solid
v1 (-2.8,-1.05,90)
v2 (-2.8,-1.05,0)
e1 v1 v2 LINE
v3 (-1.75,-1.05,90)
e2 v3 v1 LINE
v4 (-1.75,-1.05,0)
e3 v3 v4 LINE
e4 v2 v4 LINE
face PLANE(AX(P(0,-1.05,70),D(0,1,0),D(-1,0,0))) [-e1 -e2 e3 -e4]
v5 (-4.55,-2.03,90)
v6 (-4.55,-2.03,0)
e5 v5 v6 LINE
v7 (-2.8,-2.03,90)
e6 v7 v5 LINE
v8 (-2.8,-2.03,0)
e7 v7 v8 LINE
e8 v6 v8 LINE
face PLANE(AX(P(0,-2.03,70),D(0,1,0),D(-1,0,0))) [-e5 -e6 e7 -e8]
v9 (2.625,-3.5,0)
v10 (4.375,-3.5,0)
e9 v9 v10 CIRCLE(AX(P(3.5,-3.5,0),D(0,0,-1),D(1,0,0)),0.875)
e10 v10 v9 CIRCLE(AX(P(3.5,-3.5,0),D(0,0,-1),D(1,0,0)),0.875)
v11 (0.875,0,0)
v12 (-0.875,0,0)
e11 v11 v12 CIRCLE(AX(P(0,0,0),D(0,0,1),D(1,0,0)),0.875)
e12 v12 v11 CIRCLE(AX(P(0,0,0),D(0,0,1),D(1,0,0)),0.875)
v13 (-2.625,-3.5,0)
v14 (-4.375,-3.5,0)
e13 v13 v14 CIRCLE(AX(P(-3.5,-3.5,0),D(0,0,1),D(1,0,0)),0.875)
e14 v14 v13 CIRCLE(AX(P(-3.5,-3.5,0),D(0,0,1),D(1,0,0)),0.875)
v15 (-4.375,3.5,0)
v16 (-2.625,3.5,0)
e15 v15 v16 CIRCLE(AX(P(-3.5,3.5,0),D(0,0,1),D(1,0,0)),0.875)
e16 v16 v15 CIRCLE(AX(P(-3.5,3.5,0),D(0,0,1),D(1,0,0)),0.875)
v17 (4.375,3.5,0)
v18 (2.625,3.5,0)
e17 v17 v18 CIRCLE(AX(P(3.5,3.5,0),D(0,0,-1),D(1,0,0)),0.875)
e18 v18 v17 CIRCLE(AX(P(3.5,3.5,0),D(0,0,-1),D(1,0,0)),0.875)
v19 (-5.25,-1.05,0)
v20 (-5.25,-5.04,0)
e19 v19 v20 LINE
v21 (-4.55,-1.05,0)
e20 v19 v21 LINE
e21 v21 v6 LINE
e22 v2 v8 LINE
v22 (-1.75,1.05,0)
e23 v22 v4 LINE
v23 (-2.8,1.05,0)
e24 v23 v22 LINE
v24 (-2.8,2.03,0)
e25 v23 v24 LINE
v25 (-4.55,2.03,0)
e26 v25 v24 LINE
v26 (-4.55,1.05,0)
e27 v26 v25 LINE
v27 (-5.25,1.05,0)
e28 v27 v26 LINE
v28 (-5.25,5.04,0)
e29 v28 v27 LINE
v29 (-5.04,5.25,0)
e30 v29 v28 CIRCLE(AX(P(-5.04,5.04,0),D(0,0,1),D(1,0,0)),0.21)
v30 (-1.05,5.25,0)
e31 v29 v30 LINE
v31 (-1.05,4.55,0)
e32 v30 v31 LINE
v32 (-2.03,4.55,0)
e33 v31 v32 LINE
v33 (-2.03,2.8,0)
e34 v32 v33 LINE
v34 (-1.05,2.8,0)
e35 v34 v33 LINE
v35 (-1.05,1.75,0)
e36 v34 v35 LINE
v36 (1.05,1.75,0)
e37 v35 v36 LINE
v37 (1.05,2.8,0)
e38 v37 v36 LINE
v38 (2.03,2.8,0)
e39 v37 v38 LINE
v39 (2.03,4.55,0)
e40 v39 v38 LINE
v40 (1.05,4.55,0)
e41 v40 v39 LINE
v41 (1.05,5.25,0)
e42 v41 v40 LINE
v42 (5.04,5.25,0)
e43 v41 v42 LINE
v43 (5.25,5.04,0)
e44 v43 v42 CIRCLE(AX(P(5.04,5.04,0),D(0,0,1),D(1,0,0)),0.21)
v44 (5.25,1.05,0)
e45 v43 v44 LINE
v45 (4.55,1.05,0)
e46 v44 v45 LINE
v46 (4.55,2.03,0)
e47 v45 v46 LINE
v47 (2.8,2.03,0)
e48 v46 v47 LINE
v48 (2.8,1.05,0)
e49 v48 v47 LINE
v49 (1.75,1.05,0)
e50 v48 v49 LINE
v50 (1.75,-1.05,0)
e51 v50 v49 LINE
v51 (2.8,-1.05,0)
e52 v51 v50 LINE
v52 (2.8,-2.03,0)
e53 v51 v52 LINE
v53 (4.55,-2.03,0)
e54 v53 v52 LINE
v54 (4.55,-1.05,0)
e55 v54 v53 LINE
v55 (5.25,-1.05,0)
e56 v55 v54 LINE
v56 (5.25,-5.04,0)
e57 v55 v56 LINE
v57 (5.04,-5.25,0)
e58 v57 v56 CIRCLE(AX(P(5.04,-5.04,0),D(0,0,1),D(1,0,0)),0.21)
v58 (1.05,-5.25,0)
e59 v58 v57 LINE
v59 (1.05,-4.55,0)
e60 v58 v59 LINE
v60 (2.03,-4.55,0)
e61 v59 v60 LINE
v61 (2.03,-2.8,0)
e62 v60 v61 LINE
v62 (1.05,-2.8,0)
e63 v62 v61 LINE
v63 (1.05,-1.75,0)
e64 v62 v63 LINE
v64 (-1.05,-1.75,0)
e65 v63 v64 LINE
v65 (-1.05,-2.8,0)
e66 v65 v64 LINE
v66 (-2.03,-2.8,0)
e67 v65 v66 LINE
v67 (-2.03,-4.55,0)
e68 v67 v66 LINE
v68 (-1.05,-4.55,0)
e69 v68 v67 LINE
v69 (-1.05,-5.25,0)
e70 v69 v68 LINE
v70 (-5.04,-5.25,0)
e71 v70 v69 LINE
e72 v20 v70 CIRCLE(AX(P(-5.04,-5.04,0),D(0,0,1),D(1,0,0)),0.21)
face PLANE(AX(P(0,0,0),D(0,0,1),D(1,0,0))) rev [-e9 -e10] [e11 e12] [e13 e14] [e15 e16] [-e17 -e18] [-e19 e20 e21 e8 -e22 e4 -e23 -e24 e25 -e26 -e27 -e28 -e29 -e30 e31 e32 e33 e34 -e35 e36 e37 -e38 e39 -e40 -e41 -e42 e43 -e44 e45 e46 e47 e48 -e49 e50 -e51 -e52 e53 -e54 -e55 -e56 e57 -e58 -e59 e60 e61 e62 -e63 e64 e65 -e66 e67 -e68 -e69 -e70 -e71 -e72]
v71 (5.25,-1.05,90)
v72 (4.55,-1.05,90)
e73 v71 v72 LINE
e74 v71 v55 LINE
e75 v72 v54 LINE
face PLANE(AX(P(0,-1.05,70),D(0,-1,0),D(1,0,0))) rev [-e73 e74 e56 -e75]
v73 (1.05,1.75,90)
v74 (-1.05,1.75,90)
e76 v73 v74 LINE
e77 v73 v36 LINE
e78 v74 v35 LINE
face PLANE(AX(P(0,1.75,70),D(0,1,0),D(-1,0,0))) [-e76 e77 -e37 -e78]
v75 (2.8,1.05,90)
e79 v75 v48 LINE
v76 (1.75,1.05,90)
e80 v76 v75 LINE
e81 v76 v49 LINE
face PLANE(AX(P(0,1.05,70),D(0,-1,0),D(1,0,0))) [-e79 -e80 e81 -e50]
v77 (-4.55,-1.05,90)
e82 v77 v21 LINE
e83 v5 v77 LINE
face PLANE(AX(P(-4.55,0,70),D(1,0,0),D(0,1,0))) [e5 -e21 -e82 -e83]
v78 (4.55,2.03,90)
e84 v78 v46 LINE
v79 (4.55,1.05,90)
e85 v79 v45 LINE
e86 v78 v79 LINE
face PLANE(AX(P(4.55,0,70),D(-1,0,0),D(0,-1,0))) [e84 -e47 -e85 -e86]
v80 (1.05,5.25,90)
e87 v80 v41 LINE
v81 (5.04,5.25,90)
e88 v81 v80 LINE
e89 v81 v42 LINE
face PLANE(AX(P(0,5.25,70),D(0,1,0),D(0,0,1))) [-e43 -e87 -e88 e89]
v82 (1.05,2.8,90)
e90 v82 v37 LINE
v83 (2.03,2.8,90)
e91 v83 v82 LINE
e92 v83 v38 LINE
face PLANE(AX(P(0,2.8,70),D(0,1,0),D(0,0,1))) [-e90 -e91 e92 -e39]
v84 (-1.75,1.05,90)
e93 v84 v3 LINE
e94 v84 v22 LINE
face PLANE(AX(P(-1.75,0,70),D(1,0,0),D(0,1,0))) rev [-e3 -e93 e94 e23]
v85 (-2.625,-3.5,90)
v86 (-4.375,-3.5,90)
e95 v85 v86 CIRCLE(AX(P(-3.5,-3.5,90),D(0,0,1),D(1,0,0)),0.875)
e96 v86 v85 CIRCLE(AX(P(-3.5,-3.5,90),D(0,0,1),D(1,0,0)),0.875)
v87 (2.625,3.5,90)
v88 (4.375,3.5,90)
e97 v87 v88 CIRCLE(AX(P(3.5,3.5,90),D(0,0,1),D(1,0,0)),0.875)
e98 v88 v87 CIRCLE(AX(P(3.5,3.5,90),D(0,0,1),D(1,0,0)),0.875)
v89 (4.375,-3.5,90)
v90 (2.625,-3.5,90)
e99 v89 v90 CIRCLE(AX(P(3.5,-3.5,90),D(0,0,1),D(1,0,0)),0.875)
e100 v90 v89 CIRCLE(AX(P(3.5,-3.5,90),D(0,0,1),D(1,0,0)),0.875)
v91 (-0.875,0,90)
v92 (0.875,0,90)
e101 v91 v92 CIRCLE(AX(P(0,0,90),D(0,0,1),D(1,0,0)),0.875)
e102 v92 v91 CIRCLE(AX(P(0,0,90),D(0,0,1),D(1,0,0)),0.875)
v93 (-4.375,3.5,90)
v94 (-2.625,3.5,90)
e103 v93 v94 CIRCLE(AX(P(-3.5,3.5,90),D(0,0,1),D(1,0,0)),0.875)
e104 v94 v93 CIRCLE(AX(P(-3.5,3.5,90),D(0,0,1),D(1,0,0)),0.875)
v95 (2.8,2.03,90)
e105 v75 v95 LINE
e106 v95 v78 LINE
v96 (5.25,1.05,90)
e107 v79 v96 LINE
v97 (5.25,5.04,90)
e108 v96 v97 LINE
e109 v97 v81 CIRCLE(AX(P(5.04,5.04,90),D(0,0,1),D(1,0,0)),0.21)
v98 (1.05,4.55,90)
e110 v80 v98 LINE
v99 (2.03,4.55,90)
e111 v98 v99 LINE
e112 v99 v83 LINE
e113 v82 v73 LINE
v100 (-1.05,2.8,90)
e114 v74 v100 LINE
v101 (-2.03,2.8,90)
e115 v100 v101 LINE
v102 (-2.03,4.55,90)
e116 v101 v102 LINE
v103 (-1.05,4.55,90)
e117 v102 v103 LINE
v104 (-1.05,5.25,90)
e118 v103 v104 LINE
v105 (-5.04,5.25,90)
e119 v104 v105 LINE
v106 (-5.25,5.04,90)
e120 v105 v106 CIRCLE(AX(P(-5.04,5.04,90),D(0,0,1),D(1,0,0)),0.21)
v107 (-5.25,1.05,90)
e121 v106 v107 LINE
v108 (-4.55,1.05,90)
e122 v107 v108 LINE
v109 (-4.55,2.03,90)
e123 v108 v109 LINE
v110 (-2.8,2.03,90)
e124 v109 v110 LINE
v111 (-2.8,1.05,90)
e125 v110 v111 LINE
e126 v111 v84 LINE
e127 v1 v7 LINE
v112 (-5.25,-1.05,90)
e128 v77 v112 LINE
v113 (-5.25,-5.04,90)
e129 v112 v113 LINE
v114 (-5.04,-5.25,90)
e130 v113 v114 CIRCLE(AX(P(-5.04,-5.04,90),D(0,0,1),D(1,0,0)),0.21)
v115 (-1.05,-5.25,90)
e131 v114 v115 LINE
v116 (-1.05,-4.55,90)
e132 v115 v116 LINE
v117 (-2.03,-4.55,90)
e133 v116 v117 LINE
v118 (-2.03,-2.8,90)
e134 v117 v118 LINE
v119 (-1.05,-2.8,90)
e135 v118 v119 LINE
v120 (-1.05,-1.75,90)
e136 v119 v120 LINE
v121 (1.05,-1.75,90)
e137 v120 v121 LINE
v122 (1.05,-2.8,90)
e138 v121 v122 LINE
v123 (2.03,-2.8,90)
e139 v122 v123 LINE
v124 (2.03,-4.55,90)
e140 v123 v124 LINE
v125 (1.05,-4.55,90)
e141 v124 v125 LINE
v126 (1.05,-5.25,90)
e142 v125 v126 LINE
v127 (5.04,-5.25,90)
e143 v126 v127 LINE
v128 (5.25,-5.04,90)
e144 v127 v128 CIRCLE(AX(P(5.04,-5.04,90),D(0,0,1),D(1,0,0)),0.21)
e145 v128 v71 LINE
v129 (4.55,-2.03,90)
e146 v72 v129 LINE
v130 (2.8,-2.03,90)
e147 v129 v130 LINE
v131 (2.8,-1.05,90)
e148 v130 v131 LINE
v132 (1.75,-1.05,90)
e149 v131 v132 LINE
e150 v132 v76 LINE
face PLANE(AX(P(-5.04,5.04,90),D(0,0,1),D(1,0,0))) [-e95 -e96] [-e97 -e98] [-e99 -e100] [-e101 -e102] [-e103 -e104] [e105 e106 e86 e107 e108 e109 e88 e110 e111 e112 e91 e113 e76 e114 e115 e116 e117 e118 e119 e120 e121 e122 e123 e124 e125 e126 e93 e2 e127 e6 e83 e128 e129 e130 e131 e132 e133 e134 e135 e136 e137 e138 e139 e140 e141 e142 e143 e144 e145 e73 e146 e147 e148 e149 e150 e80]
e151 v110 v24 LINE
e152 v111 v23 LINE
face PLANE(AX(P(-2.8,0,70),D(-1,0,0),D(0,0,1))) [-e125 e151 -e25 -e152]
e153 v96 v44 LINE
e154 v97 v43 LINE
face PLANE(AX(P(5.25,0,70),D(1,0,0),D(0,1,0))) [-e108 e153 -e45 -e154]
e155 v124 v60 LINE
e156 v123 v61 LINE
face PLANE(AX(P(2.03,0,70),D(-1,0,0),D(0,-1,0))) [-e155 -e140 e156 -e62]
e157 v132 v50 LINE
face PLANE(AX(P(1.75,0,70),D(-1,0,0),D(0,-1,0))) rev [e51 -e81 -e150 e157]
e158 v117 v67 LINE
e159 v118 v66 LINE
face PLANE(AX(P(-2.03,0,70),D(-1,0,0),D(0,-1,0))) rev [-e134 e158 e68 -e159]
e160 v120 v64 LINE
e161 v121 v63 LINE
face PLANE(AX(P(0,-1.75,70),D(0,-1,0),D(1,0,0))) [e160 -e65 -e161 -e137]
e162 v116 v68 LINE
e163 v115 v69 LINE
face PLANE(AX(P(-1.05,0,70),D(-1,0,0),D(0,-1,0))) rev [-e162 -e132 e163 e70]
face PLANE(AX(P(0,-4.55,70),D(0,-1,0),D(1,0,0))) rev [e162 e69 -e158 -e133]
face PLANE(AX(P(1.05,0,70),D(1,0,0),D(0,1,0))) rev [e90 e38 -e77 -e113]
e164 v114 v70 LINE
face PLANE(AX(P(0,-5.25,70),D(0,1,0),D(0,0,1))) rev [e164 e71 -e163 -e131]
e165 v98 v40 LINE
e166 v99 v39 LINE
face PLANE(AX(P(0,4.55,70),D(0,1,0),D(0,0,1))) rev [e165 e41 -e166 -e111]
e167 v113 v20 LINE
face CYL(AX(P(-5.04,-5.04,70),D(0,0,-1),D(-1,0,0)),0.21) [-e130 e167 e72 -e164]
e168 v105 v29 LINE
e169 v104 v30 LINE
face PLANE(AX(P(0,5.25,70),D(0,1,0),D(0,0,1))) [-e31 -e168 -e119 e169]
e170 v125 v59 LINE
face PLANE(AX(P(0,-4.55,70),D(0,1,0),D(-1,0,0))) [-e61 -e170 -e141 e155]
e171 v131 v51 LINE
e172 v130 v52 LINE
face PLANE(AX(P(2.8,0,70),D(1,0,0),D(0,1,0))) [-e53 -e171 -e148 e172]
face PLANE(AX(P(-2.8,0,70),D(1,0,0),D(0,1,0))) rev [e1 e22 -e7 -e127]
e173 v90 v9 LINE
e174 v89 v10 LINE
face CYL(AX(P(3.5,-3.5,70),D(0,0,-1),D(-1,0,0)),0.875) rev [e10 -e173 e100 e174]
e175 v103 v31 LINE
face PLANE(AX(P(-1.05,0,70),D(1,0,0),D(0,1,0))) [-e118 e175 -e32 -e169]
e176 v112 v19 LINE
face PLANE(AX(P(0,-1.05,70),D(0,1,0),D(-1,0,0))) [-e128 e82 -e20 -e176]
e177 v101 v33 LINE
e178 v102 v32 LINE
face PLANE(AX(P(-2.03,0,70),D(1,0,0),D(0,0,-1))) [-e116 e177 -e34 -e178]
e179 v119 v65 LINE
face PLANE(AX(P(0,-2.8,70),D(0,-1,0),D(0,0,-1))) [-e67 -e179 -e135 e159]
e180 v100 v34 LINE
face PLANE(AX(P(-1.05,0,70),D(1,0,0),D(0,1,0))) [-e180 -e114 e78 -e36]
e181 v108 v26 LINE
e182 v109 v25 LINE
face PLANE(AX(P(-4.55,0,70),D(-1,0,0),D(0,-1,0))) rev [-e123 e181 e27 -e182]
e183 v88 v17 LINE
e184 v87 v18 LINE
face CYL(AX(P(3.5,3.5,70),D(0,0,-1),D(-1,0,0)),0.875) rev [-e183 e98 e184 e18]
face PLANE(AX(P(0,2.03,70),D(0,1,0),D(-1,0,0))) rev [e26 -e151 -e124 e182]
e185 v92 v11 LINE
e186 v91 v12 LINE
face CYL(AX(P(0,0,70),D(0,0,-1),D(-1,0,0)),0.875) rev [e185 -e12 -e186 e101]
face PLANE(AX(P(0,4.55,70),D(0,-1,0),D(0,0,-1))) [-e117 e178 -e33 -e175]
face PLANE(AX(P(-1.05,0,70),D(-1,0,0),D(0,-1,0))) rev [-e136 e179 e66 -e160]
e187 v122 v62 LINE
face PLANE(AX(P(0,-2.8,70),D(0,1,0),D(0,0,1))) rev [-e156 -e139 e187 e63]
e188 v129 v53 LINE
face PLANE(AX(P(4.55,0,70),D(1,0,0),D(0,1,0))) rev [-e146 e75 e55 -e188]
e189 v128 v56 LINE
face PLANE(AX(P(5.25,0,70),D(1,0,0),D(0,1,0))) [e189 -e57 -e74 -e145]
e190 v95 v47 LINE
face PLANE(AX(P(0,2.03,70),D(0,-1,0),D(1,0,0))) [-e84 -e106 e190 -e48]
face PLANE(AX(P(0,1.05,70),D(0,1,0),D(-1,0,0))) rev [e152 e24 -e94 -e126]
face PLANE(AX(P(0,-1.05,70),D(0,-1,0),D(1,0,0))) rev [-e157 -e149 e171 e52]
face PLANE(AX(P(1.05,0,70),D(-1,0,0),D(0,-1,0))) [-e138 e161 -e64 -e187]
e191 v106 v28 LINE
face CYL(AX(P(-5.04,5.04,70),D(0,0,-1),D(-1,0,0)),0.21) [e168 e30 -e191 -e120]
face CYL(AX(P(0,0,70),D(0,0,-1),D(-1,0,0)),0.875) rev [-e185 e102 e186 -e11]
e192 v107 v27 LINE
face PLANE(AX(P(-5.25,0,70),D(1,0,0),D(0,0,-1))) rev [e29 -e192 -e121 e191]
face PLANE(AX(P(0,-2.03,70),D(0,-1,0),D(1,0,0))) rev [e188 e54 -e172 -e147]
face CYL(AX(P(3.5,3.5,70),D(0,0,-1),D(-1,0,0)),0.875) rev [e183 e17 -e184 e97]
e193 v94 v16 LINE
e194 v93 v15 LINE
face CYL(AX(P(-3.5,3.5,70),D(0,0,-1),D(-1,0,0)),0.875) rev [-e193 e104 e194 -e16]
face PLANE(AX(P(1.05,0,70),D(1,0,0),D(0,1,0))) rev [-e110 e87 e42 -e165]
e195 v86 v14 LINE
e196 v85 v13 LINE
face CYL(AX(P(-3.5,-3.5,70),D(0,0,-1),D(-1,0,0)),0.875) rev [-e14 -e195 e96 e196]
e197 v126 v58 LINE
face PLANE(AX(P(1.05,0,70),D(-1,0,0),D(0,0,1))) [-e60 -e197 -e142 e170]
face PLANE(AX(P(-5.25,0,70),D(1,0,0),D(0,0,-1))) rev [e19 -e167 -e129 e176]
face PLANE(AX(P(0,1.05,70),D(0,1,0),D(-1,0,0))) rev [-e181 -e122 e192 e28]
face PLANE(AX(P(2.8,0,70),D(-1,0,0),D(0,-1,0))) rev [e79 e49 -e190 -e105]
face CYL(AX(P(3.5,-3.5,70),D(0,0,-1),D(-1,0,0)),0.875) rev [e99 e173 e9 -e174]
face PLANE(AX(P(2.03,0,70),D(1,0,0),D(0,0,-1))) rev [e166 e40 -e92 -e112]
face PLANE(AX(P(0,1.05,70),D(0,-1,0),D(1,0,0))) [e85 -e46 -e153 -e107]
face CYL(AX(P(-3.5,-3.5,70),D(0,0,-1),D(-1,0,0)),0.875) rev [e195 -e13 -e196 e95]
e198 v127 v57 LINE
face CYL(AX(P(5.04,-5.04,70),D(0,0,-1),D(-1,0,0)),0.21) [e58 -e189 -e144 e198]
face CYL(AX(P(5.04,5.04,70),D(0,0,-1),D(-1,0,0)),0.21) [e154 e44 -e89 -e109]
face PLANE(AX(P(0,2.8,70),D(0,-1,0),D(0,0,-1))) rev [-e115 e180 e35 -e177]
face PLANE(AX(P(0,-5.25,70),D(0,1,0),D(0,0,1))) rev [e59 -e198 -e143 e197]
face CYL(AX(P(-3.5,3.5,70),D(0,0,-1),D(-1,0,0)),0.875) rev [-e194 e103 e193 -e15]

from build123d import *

# Parameters (mm, degrees)
SKETCH4_R           = 1.25
BOSS_EXTRUDE3_DEPTH = 100
SCALE_1_SCALE       = 0.7
SKETCH5_R           = 0.875
BOSS_EXTRUDE4_DEPTH = 20


with BuildPart() as part:
    # Sketch4 → Boss-Extrude3 (new body)
    with BuildSketch(Plane.XY):
        with BuildLine():
            Line((-1.5, 7.5), (-7.2, 7.5))
            ThreePointArc((-7.2, 7.5), (-7.412132034, 7.412132034), (-7.5, 7.2))
            Line((-7.5, 7.2), (-7.5, 1.5))
            Line((-7.5, 1.5), (-6.5, 1.5))
            Line((-6.5, 1.5), (-6.5, 2.9))
            Line((-6.5, 2.9), (-4, 2.9))
            Line((-4, 2.9), (-4, 1.5))
            Line((-4, 1.5), (-2.5, 1.5))
            Line((-2.5, 1.5), (-2.5, -1.5))
            Line((-2.5, -1.5), (-4, -1.5))
            Line((-4, -1.5), (-4, -2.9))
            Line((-4, -2.9), (-6.5, -2.9))
            Line((-6.5, -2.9), (-6.5, -1.5))
            Line((-6.5, -1.5), (-7.5, -1.5))
            Line((-7.5, -1.5), (-7.5, -7.2))
            ThreePointArc((-7.5, -7.2), (-7.412132034, -7.412132034), (-7.2, -7.5))
            Line((-7.2, -7.5), (-1.5, -7.5))
            Line((-1.5, -7.5), (-1.5, -6.5))
            Line((-1.5, -6.5), (-2.9, -6.5))
            Line((-2.9, -6.5), (-2.9, -4))
            Line((-2.9, -4), (-1.5, -4))
            Line((-1.5, -4), (-1.5, -2.5))
            Line((-1.5, -2.5), (1.5, -2.5))
            Line((1.5, -2.5), (1.5, -4))
            Line((1.5, -4), (2.9, -4))
            Line((2.9, -4), (2.9, -6.5))
            Line((2.9, -6.5), (1.5, -6.5))
            Line((1.5, -6.5), (1.5, -7.5))
            Line((1.5, -7.5), (7.2, -7.5))
            ThreePointArc((7.2, -7.5), (7.412132034, -7.412132034), (7.5, -7.2))
            Line((7.5, -7.2), (7.5, -1.5))
            Line((7.5, -1.5), (6.5, -1.5))
            Line((6.5, -1.5), (6.5, -2.9))
            Line((6.5, -2.9), (4, -2.9))
            Line((4, -2.9), (4, -1.5))
            Line((4, -1.5), (2.5, -1.5))
            Line((2.5, -1.5), (2.5, 1.5))
            Line((2.5, 1.5), (4, 1.5))
            Line((4, 1.5), (4, 2.9))
            Line((4, 2.9), (6.5, 2.9))
            Line((6.5, 2.9), (6.5, 1.5))
            Line((6.5, 1.5), (7.5, 1.5))
            Line((7.5, 1.5), (7.5, 7.2))
            ThreePointArc((7.5, 7.2), (7.412132034, 7.412132034), (7.2, 7.5))
            Line((7.2, 7.5), (1.5, 7.5))
            Line((1.5, 7.5), (1.5, 6.5))
            Line((1.5, 6.5), (2.9, 6.5))
            Line((2.9, 6.5), (2.9, 4))
            Line((2.9, 4), (1.5, 4))
            Line((1.5, 4), (1.5, 2.5))
            Line((1.5, 2.5), (-1.5, 2.5))
            Line((-1.5, 2.5), (-1.5, 4))
            Line((-1.5, 4), (-2.9, 4))
            Line((-2.9, 4), (-2.9, 6.5))
            Line((-2.9, 6.5), (-1.5, 6.5))
            Line((-1.5, 6.5), (-1.5, 7.5))
        make_face()
        with Locations((-5, -5)):
            Circle(SKETCH4_R, mode=Mode.SUBTRACT)
        Circle(SKETCH4_R, mode=Mode.SUBTRACT)
        with Locations((5, -5)):
            Circle(SKETCH4_R, mode=Mode.SUBTRACT)
        with Locations((-5, 5)):
            Circle(SKETCH4_R, mode=Mode.SUBTRACT)
        with Locations((5, 5)):
            Circle(SKETCH4_R, mode=Mode.SUBTRACT)
    extrude(amount=BOSS_EXTRUDE3_DEPTH)


with BuildPart() as part_1:
    # Scale 1: scaled about (0, 0, 0)
    add(part.part.scale(SCALE_1_SCALE))

    # Sketch5 → Boss-Extrude4 (add)
    with BuildSketch(Plane.XY.offset(70)):
        with BuildLine():
            Line((-1.05, 5.25), (-5.04, 5.25))
            ThreePointArc((-5.04, 5.25), (-5.188492424, 5.188492424), (-5.25, 5.04))
            Line((-5.25, 5.04), (-5.25, 1.05))
            Line((-5.25, 1.05), (-4.55, 1.05))
            Line((-4.55, 1.05), (-4.55, 2.03))
            Line((-4.55, 2.03), (-2.8, 2.03))
            Line((-2.8, 2.03), (-2.8, 1.05))
            Line((-2.8, 1.05), (-1.75, 1.05))
            Line((-1.75, 1.05), (-1.75, -1.05))
            Line((-1.75, -1.05), (-2.8, -1.05))
            Line((-2.8, -1.05), (-2.8, -2.03))
            Line((-2.8, -2.03), (-4.55, -2.03))
            Line((-4.55, -2.03), (-4.55, -1.05))
            Line((-4.55, -1.05), (-5.25, -1.05))
            Line((-5.25, -1.05), (-5.25, -5.04))
            ThreePointArc((-5.25, -5.04), (-5.188492424, -5.188492424), (-5.04, -5.25))
            Line((-5.04, -5.25), (-1.05, -5.25))
            Line((-1.05, -5.25), (-1.05, -4.55))
            Line((-1.05, -4.55), (-2.03, -4.55))
            Line((-2.03, -4.55), (-2.03, -2.8))
            Line((-2.03, -2.8), (-1.05, -2.8))
            Line((-1.05, -2.8), (-1.05, -1.75))
            Line((-1.05, -1.75), (1.05, -1.75))
            Line((1.05, -1.75), (1.05, -2.8))
            Line((1.05, -2.8), (2.03, -2.8))
            Line((2.03, -2.8), (2.03, -4.55))
            Line((2.03, -4.55), (1.05, -4.55))
            Line((1.05, -4.55), (1.05, -5.25))
            Line((1.05, -5.25), (5.04, -5.25))
            ThreePointArc((5.04, -5.25), (5.188492424, -5.188492424), (5.25, -5.04))
            Line((5.25, -5.04), (5.25, -1.05))
            Line((5.25, -1.05), (4.55, -1.05))
            Line((4.55, -1.05), (4.55, -2.03))
            Line((4.55, -2.03), (2.8, -2.03))
            Line((2.8, -2.03), (2.8, -1.05))
            Line((2.8, -1.05), (1.75, -1.05))
            Line((1.75, -1.05), (1.75, 1.05))
            Line((1.75, 1.05), (2.8, 1.05))
            Line((2.8, 1.05), (2.8, 2.03))
            Line((2.8, 2.03), (4.55, 2.03))
            Line((4.55, 2.03), (4.55, 1.05))
            Line((4.55, 1.05), (5.25, 1.05))
            Line((5.25, 1.05), (5.25, 5.04))
            ThreePointArc((5.25, 5.04), (5.188492424, 5.188492424), (5.04, 5.25))
            Line((5.04, 5.25), (1.05, 5.25))
            Line((1.05, 5.25), (1.05, 4.55))
            Line((1.05, 4.55), (2.03, 4.55))
            Line((2.03, 4.55), (2.03, 2.8))
            Line((2.03, 2.8), (1.05, 2.8))
            Line((1.05, 2.8), (1.05, 1.75))
            Line((1.05, 1.75), (-1.05, 1.75))
            Line((-1.05, 1.75), (-1.05, 2.8))
            Line((-1.05, 2.8), (-2.03, 2.8))
            Line((-2.03, 2.8), (-2.03, 4.55))
            Line((-2.03, 4.55), (-1.05, 4.55))
            Line((-1.05, 4.55), (-1.05, 5.25))
        make_face()
        with Locations((3.5, -3.5)):
            Circle(SKETCH5_R, mode=Mode.SUBTRACT)
        with Locations((-3.5, -3.5)):
            Circle(SKETCH5_R, mode=Mode.SUBTRACT)
        with Locations((-3.5, 3.5)):
            Circle(SKETCH5_R, mode=Mode.SUBTRACT)
        with Locations((3.5, 3.5)):
            Circle(SKETCH5_R, mode=Mode.SUBTRACT)
        Circle(SKETCH5_R, mode=Mode.SUBTRACT)
    extrude(amount=BOSS_EXTRUDE4_DEPTH)


solid = part_1.part
